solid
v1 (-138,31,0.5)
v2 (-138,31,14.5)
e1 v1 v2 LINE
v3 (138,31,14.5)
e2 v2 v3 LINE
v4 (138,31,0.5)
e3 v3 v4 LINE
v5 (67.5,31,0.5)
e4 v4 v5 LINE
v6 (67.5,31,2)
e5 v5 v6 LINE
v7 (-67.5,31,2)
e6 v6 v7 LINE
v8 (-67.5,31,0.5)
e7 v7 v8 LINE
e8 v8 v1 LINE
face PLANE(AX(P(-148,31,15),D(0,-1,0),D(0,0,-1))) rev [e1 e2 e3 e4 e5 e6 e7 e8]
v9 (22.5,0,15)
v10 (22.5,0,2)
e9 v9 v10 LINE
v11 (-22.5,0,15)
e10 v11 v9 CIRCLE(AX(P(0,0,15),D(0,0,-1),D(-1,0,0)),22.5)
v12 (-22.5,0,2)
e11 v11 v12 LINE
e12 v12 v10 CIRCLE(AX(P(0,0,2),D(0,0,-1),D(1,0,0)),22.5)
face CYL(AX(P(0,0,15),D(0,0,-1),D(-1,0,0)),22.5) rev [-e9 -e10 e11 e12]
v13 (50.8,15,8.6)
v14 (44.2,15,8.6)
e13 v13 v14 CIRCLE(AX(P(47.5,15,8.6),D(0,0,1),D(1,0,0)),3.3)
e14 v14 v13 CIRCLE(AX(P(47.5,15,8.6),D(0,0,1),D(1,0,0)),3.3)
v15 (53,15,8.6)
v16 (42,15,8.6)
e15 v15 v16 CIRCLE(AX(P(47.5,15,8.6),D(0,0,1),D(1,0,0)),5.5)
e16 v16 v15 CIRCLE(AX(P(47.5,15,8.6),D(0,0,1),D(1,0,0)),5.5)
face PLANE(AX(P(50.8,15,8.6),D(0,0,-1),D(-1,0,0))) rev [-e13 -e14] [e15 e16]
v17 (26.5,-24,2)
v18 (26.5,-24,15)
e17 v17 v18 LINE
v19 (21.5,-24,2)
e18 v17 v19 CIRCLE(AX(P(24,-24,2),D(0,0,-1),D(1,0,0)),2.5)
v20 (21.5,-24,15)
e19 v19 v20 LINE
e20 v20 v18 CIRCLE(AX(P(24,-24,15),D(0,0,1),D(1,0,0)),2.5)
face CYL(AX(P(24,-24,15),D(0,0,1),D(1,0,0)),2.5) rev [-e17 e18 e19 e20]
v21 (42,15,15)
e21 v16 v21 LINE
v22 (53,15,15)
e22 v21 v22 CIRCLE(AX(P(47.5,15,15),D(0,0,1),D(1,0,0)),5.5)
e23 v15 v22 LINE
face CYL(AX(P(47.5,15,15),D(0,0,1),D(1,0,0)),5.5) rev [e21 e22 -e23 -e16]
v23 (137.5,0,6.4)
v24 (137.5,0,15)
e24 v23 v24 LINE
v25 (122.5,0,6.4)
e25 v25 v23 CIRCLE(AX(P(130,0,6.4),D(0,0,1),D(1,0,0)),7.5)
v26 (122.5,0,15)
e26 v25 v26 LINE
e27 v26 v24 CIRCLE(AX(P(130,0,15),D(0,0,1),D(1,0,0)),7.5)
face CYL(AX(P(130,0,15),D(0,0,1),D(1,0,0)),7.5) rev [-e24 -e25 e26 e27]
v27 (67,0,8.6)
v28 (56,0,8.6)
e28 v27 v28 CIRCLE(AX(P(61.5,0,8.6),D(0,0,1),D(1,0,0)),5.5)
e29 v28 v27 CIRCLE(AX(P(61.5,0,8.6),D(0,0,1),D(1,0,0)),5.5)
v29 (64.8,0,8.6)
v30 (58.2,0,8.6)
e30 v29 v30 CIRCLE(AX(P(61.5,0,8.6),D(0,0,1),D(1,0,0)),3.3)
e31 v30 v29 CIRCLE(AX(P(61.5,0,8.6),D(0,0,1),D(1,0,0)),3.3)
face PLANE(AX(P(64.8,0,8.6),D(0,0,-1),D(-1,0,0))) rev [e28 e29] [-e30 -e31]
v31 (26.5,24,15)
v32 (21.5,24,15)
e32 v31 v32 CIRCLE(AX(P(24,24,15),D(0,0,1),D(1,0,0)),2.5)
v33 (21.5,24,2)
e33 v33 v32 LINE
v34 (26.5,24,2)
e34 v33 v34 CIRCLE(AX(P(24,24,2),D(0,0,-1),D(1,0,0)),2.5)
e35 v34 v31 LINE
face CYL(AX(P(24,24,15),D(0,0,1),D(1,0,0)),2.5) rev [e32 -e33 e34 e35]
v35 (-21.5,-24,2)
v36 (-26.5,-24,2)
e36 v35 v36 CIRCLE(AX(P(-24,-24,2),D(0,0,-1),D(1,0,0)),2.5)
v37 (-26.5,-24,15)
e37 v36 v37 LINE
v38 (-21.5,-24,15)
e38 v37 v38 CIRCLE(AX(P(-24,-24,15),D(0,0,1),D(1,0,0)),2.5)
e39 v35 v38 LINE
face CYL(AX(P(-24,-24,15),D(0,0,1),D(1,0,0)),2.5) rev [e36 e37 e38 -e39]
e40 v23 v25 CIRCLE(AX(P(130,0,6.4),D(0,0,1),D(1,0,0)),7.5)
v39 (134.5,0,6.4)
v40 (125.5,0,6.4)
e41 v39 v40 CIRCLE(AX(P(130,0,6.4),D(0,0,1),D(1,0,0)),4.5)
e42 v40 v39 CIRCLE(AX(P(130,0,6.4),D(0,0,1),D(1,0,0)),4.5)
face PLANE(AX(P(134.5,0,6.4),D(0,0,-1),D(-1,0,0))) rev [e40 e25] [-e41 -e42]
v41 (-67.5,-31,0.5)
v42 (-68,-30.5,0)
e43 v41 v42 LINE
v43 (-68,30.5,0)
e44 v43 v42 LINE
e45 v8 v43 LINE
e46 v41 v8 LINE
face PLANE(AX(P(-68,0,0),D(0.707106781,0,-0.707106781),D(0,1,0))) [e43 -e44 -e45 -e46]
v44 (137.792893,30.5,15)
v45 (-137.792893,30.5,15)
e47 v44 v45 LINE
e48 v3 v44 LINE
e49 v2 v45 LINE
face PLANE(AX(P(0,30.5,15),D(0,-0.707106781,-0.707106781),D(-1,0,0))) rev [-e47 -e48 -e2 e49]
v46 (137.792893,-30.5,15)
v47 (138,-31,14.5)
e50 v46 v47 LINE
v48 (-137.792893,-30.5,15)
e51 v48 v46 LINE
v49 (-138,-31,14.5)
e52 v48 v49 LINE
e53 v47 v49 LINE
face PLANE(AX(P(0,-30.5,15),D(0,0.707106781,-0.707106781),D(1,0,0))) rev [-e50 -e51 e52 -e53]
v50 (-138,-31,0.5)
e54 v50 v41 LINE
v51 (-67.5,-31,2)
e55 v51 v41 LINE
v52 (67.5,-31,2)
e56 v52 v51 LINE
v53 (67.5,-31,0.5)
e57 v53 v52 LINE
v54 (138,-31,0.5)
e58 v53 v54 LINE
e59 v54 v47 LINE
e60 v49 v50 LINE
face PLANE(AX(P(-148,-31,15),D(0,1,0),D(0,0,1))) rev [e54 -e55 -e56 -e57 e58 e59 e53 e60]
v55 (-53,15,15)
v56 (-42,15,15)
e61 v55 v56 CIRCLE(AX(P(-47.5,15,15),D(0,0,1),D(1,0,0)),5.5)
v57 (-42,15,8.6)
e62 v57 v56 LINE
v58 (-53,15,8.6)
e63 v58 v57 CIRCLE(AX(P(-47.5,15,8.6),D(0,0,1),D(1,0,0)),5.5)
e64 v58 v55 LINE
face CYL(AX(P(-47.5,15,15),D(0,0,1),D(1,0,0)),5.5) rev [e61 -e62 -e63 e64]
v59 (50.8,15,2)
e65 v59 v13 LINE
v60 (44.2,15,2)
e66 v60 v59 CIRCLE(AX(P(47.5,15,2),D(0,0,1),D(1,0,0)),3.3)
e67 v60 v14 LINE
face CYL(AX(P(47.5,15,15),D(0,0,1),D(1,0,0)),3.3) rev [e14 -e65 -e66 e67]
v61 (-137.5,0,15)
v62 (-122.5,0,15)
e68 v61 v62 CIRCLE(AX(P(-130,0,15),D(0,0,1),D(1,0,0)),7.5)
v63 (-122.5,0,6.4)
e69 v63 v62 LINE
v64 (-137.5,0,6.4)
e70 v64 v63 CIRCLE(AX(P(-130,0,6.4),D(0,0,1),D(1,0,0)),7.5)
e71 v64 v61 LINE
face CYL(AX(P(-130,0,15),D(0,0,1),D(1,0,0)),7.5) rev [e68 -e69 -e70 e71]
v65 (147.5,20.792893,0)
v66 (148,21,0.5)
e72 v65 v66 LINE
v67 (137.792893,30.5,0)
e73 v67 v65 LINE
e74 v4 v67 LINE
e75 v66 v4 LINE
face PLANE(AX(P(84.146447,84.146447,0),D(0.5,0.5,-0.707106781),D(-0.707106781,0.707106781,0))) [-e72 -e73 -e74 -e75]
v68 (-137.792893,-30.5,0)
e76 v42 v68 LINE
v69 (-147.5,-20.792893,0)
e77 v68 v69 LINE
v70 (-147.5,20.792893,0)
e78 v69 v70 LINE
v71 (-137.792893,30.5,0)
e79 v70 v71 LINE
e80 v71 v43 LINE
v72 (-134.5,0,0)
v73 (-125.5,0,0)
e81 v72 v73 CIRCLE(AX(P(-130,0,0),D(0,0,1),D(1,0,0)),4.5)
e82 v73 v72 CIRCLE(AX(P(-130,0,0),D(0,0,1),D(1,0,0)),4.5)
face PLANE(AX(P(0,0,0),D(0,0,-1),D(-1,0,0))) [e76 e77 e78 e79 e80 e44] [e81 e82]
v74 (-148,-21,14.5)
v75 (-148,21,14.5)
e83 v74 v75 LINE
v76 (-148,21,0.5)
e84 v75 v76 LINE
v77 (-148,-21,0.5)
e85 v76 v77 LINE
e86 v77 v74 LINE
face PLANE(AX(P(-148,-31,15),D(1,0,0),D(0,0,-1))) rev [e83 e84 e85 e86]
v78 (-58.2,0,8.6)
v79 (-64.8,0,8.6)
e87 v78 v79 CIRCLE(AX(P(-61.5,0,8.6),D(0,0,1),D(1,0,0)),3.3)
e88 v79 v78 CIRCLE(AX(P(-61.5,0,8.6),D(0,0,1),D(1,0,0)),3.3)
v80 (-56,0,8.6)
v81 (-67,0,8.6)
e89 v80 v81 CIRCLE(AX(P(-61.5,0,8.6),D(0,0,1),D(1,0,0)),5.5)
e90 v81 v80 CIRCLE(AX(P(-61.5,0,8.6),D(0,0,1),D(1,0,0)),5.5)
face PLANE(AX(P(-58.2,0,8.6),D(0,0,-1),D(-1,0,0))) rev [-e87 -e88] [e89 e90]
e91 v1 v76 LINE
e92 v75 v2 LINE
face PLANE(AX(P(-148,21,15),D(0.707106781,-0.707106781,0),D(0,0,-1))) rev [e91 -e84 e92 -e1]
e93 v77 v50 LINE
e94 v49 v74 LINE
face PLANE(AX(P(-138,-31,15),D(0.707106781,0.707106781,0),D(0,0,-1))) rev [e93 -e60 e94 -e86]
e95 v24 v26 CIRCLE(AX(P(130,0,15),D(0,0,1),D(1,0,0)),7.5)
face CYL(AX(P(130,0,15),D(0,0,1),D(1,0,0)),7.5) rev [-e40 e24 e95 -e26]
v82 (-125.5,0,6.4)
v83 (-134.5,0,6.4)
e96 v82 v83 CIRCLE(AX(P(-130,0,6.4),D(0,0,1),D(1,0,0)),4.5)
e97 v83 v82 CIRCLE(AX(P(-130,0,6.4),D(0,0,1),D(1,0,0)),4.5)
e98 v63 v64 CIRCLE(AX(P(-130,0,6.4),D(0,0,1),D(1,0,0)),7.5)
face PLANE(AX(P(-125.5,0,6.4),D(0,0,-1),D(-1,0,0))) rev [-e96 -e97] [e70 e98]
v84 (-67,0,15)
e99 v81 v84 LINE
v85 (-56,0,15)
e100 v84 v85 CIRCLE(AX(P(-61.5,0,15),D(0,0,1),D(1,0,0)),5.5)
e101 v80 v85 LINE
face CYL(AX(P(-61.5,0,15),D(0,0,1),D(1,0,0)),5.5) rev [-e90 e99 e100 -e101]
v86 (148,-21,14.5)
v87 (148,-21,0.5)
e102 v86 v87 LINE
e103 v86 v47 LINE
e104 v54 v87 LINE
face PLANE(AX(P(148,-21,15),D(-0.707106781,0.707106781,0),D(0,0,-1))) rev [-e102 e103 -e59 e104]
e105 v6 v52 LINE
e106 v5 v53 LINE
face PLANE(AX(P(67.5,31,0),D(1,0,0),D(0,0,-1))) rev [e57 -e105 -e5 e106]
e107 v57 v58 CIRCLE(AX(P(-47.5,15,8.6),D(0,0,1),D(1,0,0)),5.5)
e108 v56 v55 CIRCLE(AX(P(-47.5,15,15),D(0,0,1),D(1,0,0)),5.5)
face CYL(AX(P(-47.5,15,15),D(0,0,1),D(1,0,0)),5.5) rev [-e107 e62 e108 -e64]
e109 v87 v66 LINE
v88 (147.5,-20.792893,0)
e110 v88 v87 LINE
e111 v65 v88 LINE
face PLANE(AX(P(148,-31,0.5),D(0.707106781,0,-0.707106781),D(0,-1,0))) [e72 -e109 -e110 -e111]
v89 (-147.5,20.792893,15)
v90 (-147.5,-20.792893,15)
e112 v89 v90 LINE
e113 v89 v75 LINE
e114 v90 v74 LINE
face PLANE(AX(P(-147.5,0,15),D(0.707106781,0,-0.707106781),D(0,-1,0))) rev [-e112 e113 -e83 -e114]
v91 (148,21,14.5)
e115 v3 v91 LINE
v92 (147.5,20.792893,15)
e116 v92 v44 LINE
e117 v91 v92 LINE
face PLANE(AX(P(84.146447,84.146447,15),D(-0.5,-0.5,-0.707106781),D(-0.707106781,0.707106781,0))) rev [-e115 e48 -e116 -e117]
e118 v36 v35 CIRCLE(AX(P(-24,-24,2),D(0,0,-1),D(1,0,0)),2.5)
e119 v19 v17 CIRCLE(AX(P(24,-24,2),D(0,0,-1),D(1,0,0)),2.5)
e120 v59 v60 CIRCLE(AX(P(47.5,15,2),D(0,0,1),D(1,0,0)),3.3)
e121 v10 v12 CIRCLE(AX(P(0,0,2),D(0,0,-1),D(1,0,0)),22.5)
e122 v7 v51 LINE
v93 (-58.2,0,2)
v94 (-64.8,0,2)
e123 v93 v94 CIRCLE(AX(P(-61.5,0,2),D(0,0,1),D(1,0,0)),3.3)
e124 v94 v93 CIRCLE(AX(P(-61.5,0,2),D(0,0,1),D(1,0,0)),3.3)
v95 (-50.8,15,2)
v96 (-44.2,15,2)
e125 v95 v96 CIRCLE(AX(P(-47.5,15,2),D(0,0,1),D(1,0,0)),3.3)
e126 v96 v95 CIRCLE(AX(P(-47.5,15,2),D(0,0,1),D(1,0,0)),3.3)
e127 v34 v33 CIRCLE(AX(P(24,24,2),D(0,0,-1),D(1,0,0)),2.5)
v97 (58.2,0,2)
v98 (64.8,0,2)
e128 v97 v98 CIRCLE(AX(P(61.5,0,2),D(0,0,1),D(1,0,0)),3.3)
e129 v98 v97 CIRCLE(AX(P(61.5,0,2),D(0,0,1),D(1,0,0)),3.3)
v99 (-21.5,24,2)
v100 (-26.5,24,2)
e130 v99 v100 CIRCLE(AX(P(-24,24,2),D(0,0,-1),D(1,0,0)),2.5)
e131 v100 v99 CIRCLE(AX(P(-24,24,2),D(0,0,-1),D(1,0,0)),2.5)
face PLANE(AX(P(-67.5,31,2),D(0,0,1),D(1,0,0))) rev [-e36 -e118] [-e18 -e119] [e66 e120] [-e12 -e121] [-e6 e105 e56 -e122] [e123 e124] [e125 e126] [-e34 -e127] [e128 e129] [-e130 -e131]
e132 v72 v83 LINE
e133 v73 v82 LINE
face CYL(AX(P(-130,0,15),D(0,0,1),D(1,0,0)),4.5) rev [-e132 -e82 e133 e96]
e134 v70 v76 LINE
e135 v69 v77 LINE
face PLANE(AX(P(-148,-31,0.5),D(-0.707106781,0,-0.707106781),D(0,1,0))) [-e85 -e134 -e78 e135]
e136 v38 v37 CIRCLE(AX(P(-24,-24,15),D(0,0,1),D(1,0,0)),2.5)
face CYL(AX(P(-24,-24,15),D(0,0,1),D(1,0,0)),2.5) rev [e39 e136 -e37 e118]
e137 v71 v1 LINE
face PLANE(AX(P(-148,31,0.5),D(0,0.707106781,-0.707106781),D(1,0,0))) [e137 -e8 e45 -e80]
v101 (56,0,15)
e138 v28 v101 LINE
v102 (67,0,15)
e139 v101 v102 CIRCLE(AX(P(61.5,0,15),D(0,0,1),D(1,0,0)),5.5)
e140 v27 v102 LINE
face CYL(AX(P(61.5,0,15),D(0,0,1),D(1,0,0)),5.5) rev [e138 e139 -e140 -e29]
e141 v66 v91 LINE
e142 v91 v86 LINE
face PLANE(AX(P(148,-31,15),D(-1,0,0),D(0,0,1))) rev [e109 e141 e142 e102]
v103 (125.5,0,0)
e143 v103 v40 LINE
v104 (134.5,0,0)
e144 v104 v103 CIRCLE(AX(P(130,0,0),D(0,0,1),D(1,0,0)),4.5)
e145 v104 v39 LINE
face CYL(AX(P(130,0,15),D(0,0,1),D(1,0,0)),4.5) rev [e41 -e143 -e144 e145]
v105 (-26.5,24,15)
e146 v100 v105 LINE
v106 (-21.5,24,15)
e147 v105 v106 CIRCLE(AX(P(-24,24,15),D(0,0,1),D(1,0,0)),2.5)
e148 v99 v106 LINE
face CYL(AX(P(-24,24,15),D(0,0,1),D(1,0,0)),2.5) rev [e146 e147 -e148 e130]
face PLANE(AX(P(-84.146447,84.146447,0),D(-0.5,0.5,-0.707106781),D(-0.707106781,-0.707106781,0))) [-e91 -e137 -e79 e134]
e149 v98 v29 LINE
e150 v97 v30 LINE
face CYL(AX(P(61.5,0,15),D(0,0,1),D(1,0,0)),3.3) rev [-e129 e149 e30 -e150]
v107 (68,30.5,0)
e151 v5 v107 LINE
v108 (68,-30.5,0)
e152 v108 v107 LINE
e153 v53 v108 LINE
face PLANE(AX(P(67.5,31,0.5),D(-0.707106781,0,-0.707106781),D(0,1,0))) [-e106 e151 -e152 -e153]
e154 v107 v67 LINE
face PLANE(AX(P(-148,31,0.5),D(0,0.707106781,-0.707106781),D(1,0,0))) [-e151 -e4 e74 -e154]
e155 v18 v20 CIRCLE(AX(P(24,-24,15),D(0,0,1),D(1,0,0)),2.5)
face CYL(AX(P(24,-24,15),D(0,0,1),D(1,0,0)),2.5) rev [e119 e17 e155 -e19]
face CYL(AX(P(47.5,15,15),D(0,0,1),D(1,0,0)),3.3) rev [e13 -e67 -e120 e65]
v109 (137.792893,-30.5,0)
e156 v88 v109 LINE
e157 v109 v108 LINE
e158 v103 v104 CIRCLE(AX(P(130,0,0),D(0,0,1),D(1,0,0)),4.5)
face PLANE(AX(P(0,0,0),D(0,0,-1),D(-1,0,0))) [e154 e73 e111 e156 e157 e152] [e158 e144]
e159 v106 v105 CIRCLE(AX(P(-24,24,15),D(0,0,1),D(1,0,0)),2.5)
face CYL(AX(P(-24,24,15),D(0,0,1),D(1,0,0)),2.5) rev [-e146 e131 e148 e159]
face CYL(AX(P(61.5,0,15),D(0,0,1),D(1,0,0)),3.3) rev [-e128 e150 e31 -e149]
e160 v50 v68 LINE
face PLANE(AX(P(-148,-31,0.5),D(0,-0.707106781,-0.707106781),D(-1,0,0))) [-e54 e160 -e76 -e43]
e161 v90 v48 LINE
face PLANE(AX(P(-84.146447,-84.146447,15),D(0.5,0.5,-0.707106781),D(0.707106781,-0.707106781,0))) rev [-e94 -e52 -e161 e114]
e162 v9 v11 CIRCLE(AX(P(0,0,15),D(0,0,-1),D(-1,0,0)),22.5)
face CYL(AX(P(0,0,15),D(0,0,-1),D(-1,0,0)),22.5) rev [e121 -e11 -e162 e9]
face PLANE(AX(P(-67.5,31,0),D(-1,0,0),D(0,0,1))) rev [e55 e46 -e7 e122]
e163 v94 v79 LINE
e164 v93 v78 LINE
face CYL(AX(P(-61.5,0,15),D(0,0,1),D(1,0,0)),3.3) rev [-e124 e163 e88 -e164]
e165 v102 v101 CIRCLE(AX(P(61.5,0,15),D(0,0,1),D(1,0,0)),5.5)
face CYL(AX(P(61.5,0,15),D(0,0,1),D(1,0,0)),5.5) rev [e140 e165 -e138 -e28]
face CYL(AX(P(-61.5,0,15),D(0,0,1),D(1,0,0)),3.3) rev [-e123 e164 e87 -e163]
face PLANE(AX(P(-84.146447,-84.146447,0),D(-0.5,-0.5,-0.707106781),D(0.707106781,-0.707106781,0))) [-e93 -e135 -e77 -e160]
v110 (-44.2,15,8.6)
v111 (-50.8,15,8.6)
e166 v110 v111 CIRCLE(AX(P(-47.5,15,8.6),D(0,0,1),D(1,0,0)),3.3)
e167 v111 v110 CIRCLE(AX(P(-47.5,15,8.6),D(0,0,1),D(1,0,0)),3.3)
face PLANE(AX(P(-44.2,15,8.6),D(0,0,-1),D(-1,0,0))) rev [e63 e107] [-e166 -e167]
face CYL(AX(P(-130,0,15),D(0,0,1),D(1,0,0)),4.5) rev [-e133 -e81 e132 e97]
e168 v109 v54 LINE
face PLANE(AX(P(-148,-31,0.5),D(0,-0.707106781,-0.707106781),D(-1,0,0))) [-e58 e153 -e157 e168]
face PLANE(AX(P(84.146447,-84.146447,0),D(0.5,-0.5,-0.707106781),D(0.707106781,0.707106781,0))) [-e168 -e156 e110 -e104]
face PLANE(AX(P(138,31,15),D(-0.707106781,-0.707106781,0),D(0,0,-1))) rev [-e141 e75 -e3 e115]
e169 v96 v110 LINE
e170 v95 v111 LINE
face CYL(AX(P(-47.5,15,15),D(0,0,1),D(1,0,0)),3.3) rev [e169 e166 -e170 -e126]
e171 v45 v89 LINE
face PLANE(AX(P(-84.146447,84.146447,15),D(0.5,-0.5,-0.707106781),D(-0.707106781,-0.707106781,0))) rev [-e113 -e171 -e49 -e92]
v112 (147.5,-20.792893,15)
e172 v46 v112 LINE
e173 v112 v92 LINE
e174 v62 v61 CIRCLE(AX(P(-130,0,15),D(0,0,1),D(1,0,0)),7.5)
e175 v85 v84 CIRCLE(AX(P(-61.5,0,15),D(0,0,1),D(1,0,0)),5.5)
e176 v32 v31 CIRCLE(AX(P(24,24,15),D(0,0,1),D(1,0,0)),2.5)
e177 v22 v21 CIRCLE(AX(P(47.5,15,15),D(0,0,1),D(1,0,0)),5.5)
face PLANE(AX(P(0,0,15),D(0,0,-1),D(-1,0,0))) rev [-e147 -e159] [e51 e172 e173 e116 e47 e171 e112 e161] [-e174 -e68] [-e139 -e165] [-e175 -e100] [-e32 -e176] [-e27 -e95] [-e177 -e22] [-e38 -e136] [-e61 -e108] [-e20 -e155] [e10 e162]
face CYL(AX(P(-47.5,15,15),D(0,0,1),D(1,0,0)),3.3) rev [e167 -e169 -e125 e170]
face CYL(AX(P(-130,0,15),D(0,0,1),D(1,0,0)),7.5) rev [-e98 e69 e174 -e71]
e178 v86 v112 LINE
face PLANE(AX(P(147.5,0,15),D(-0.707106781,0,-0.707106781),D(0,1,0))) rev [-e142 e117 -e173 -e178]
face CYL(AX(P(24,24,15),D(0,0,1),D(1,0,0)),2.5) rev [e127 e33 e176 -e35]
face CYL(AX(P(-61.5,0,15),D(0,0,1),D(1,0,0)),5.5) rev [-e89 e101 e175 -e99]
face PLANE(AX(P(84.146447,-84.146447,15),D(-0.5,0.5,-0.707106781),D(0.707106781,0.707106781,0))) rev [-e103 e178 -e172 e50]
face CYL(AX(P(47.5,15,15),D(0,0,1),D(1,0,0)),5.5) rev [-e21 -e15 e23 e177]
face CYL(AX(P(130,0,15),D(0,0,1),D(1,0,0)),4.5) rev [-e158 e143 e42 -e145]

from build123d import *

# Parameters (mm, degrees)
SKETCH_1_W                     = 296
SKETCH_1_H                     = 62
EXTRUDE_1_DEPTH                = 15
CHAMFER_1_SIZE                 = 10
SKETCH_3_R                     = 22.5
CUT_EXTRUDE_2_DEPTH            = 152.95394039
HOLE_WIZARD_M6_1_D             = 5
SKETCH_6_W                     = 135
SKETCH_6_H                     = 2
CUT_EXTRUDE_3_DEPTH            = 162.161409773
HOLE_WIZARD_M6_1_2_D           = 6.6
HOLE_WIZARD_M6_1_2_CBORE_D     = 11
HOLE_WIZARD_M6_1_2_CBORE_DEPTH = 6.4
HOLE_WIZARD_M8_1_D             = 9
HOLE_WIZARD_M8_1_CBORE_D       = 15
HOLE_WIZARD_M8_1_CBORE_DEPTH   = 8.6
CHAMFER_2_SIZE                 = 0.5


with BuildPart() as part:
    # 草图1 → 凸台-拉伸1 (new body)
    with BuildSketch(Plane.XY):
        Rectangle(SKETCH_1_W, SKETCH_1_H)
    extrude(amount=EXTRUDE_1_DEPTH)

    # 倒角1
    chamfer_1_edges = [part.edges().sort_by_distance(p)[0] for p in [
        (148, -31, 7.5),
        (-148, -31, 7.5),
        (-148, 31, 7.5),
        (148, 31, 7.5),
    ]]
    chamfer(chamfer_1_edges, length=CHAMFER_1_SIZE)

    # 草图3 → 切除-拉伸2 (cut, through all)
    with BuildSketch(Plane(origin=(0, 0, 0), x_dir=(-1, 0, 0), z_dir=(0, 0, -1))):
        Circle(SKETCH_3_R)
    extrude(amount=-CUT_EXTRUDE_2_DEPTH, mode=Mode.SUBTRACT)

    # Hole Wizard M6 _1 (through all)
    with Locations(Plane.XY.offset(15)):
        with Locations((-24, 24), (24, 24), (24, -24), (-24, -24)):
            Hole(HOLE_WIZARD_M6_1_D / 2)

    # 草图6 → 切除-拉伸3 (cut, through all)
    with BuildSketch(Plane.XZ.offset(31)):
        with Locations((0, 1)):
            Rectangle(SKETCH_6_W, SKETCH_6_H)
    extrude(amount=-CUT_EXTRUDE_3_DEPTH, mode=Mode.SUBTRACT)

    # Hole Wizard M6 _1 2 (through all)
    with Locations(Plane.XY.offset(15)):
        with Locations((-47.5, 15), (-61.5, 0), (47.5, 15), (61.5, 0)):
            CounterBoreHole(HOLE_WIZARD_M6_1_2_D / 2, HOLE_WIZARD_M6_1_2_CBORE_D / 2, HOLE_WIZARD_M6_1_2_CBORE_DEPTH)

    # M8 六角凹头螺钉的柱形沉头孔1 (through all)
    with Locations(Plane(origin=(0, 0, 15), x_dir=(-1, 0, 0), z_dir=(0, 0, 1))):
        with Locations((130, 0), (-130, 0)):
            CounterBoreHole(HOLE_WIZARD_M8_1_D / 2, HOLE_WIZARD_M8_1_CBORE_D / 2, HOLE_WIZARD_M8_1_CBORE_DEPTH)

    # 倒角2
    chamfer_2_edges = [part.edges().sort_by_distance(p)[0] for p in [
        (102.75, 31, 0),
        (0, 31, 15),
        (148, 0, 0),
        (-102.75, -31, 0),
        (-148, 0, 0),
        (-143, -26, 0),
        (-143, 26, 0),
        (143, -26, 0),
        (143, 26, 0),
        (148, 0, 15),
        (-148, 0, 15),
        (0, -31, 15),
        (-143, -26, 15),
        (-143, 26, 15),
        (143, -26, 15),
        (143, 26, 15),
        (-102.75, 31, 0),
        (102.75, -31, 0),
        (67.5, 0, 0),
        (-67.5, 0, 0),
    ]]
    chamfer(chamfer_2_edges, length=CHAMFER_2_SIZE)


solid = part.part
